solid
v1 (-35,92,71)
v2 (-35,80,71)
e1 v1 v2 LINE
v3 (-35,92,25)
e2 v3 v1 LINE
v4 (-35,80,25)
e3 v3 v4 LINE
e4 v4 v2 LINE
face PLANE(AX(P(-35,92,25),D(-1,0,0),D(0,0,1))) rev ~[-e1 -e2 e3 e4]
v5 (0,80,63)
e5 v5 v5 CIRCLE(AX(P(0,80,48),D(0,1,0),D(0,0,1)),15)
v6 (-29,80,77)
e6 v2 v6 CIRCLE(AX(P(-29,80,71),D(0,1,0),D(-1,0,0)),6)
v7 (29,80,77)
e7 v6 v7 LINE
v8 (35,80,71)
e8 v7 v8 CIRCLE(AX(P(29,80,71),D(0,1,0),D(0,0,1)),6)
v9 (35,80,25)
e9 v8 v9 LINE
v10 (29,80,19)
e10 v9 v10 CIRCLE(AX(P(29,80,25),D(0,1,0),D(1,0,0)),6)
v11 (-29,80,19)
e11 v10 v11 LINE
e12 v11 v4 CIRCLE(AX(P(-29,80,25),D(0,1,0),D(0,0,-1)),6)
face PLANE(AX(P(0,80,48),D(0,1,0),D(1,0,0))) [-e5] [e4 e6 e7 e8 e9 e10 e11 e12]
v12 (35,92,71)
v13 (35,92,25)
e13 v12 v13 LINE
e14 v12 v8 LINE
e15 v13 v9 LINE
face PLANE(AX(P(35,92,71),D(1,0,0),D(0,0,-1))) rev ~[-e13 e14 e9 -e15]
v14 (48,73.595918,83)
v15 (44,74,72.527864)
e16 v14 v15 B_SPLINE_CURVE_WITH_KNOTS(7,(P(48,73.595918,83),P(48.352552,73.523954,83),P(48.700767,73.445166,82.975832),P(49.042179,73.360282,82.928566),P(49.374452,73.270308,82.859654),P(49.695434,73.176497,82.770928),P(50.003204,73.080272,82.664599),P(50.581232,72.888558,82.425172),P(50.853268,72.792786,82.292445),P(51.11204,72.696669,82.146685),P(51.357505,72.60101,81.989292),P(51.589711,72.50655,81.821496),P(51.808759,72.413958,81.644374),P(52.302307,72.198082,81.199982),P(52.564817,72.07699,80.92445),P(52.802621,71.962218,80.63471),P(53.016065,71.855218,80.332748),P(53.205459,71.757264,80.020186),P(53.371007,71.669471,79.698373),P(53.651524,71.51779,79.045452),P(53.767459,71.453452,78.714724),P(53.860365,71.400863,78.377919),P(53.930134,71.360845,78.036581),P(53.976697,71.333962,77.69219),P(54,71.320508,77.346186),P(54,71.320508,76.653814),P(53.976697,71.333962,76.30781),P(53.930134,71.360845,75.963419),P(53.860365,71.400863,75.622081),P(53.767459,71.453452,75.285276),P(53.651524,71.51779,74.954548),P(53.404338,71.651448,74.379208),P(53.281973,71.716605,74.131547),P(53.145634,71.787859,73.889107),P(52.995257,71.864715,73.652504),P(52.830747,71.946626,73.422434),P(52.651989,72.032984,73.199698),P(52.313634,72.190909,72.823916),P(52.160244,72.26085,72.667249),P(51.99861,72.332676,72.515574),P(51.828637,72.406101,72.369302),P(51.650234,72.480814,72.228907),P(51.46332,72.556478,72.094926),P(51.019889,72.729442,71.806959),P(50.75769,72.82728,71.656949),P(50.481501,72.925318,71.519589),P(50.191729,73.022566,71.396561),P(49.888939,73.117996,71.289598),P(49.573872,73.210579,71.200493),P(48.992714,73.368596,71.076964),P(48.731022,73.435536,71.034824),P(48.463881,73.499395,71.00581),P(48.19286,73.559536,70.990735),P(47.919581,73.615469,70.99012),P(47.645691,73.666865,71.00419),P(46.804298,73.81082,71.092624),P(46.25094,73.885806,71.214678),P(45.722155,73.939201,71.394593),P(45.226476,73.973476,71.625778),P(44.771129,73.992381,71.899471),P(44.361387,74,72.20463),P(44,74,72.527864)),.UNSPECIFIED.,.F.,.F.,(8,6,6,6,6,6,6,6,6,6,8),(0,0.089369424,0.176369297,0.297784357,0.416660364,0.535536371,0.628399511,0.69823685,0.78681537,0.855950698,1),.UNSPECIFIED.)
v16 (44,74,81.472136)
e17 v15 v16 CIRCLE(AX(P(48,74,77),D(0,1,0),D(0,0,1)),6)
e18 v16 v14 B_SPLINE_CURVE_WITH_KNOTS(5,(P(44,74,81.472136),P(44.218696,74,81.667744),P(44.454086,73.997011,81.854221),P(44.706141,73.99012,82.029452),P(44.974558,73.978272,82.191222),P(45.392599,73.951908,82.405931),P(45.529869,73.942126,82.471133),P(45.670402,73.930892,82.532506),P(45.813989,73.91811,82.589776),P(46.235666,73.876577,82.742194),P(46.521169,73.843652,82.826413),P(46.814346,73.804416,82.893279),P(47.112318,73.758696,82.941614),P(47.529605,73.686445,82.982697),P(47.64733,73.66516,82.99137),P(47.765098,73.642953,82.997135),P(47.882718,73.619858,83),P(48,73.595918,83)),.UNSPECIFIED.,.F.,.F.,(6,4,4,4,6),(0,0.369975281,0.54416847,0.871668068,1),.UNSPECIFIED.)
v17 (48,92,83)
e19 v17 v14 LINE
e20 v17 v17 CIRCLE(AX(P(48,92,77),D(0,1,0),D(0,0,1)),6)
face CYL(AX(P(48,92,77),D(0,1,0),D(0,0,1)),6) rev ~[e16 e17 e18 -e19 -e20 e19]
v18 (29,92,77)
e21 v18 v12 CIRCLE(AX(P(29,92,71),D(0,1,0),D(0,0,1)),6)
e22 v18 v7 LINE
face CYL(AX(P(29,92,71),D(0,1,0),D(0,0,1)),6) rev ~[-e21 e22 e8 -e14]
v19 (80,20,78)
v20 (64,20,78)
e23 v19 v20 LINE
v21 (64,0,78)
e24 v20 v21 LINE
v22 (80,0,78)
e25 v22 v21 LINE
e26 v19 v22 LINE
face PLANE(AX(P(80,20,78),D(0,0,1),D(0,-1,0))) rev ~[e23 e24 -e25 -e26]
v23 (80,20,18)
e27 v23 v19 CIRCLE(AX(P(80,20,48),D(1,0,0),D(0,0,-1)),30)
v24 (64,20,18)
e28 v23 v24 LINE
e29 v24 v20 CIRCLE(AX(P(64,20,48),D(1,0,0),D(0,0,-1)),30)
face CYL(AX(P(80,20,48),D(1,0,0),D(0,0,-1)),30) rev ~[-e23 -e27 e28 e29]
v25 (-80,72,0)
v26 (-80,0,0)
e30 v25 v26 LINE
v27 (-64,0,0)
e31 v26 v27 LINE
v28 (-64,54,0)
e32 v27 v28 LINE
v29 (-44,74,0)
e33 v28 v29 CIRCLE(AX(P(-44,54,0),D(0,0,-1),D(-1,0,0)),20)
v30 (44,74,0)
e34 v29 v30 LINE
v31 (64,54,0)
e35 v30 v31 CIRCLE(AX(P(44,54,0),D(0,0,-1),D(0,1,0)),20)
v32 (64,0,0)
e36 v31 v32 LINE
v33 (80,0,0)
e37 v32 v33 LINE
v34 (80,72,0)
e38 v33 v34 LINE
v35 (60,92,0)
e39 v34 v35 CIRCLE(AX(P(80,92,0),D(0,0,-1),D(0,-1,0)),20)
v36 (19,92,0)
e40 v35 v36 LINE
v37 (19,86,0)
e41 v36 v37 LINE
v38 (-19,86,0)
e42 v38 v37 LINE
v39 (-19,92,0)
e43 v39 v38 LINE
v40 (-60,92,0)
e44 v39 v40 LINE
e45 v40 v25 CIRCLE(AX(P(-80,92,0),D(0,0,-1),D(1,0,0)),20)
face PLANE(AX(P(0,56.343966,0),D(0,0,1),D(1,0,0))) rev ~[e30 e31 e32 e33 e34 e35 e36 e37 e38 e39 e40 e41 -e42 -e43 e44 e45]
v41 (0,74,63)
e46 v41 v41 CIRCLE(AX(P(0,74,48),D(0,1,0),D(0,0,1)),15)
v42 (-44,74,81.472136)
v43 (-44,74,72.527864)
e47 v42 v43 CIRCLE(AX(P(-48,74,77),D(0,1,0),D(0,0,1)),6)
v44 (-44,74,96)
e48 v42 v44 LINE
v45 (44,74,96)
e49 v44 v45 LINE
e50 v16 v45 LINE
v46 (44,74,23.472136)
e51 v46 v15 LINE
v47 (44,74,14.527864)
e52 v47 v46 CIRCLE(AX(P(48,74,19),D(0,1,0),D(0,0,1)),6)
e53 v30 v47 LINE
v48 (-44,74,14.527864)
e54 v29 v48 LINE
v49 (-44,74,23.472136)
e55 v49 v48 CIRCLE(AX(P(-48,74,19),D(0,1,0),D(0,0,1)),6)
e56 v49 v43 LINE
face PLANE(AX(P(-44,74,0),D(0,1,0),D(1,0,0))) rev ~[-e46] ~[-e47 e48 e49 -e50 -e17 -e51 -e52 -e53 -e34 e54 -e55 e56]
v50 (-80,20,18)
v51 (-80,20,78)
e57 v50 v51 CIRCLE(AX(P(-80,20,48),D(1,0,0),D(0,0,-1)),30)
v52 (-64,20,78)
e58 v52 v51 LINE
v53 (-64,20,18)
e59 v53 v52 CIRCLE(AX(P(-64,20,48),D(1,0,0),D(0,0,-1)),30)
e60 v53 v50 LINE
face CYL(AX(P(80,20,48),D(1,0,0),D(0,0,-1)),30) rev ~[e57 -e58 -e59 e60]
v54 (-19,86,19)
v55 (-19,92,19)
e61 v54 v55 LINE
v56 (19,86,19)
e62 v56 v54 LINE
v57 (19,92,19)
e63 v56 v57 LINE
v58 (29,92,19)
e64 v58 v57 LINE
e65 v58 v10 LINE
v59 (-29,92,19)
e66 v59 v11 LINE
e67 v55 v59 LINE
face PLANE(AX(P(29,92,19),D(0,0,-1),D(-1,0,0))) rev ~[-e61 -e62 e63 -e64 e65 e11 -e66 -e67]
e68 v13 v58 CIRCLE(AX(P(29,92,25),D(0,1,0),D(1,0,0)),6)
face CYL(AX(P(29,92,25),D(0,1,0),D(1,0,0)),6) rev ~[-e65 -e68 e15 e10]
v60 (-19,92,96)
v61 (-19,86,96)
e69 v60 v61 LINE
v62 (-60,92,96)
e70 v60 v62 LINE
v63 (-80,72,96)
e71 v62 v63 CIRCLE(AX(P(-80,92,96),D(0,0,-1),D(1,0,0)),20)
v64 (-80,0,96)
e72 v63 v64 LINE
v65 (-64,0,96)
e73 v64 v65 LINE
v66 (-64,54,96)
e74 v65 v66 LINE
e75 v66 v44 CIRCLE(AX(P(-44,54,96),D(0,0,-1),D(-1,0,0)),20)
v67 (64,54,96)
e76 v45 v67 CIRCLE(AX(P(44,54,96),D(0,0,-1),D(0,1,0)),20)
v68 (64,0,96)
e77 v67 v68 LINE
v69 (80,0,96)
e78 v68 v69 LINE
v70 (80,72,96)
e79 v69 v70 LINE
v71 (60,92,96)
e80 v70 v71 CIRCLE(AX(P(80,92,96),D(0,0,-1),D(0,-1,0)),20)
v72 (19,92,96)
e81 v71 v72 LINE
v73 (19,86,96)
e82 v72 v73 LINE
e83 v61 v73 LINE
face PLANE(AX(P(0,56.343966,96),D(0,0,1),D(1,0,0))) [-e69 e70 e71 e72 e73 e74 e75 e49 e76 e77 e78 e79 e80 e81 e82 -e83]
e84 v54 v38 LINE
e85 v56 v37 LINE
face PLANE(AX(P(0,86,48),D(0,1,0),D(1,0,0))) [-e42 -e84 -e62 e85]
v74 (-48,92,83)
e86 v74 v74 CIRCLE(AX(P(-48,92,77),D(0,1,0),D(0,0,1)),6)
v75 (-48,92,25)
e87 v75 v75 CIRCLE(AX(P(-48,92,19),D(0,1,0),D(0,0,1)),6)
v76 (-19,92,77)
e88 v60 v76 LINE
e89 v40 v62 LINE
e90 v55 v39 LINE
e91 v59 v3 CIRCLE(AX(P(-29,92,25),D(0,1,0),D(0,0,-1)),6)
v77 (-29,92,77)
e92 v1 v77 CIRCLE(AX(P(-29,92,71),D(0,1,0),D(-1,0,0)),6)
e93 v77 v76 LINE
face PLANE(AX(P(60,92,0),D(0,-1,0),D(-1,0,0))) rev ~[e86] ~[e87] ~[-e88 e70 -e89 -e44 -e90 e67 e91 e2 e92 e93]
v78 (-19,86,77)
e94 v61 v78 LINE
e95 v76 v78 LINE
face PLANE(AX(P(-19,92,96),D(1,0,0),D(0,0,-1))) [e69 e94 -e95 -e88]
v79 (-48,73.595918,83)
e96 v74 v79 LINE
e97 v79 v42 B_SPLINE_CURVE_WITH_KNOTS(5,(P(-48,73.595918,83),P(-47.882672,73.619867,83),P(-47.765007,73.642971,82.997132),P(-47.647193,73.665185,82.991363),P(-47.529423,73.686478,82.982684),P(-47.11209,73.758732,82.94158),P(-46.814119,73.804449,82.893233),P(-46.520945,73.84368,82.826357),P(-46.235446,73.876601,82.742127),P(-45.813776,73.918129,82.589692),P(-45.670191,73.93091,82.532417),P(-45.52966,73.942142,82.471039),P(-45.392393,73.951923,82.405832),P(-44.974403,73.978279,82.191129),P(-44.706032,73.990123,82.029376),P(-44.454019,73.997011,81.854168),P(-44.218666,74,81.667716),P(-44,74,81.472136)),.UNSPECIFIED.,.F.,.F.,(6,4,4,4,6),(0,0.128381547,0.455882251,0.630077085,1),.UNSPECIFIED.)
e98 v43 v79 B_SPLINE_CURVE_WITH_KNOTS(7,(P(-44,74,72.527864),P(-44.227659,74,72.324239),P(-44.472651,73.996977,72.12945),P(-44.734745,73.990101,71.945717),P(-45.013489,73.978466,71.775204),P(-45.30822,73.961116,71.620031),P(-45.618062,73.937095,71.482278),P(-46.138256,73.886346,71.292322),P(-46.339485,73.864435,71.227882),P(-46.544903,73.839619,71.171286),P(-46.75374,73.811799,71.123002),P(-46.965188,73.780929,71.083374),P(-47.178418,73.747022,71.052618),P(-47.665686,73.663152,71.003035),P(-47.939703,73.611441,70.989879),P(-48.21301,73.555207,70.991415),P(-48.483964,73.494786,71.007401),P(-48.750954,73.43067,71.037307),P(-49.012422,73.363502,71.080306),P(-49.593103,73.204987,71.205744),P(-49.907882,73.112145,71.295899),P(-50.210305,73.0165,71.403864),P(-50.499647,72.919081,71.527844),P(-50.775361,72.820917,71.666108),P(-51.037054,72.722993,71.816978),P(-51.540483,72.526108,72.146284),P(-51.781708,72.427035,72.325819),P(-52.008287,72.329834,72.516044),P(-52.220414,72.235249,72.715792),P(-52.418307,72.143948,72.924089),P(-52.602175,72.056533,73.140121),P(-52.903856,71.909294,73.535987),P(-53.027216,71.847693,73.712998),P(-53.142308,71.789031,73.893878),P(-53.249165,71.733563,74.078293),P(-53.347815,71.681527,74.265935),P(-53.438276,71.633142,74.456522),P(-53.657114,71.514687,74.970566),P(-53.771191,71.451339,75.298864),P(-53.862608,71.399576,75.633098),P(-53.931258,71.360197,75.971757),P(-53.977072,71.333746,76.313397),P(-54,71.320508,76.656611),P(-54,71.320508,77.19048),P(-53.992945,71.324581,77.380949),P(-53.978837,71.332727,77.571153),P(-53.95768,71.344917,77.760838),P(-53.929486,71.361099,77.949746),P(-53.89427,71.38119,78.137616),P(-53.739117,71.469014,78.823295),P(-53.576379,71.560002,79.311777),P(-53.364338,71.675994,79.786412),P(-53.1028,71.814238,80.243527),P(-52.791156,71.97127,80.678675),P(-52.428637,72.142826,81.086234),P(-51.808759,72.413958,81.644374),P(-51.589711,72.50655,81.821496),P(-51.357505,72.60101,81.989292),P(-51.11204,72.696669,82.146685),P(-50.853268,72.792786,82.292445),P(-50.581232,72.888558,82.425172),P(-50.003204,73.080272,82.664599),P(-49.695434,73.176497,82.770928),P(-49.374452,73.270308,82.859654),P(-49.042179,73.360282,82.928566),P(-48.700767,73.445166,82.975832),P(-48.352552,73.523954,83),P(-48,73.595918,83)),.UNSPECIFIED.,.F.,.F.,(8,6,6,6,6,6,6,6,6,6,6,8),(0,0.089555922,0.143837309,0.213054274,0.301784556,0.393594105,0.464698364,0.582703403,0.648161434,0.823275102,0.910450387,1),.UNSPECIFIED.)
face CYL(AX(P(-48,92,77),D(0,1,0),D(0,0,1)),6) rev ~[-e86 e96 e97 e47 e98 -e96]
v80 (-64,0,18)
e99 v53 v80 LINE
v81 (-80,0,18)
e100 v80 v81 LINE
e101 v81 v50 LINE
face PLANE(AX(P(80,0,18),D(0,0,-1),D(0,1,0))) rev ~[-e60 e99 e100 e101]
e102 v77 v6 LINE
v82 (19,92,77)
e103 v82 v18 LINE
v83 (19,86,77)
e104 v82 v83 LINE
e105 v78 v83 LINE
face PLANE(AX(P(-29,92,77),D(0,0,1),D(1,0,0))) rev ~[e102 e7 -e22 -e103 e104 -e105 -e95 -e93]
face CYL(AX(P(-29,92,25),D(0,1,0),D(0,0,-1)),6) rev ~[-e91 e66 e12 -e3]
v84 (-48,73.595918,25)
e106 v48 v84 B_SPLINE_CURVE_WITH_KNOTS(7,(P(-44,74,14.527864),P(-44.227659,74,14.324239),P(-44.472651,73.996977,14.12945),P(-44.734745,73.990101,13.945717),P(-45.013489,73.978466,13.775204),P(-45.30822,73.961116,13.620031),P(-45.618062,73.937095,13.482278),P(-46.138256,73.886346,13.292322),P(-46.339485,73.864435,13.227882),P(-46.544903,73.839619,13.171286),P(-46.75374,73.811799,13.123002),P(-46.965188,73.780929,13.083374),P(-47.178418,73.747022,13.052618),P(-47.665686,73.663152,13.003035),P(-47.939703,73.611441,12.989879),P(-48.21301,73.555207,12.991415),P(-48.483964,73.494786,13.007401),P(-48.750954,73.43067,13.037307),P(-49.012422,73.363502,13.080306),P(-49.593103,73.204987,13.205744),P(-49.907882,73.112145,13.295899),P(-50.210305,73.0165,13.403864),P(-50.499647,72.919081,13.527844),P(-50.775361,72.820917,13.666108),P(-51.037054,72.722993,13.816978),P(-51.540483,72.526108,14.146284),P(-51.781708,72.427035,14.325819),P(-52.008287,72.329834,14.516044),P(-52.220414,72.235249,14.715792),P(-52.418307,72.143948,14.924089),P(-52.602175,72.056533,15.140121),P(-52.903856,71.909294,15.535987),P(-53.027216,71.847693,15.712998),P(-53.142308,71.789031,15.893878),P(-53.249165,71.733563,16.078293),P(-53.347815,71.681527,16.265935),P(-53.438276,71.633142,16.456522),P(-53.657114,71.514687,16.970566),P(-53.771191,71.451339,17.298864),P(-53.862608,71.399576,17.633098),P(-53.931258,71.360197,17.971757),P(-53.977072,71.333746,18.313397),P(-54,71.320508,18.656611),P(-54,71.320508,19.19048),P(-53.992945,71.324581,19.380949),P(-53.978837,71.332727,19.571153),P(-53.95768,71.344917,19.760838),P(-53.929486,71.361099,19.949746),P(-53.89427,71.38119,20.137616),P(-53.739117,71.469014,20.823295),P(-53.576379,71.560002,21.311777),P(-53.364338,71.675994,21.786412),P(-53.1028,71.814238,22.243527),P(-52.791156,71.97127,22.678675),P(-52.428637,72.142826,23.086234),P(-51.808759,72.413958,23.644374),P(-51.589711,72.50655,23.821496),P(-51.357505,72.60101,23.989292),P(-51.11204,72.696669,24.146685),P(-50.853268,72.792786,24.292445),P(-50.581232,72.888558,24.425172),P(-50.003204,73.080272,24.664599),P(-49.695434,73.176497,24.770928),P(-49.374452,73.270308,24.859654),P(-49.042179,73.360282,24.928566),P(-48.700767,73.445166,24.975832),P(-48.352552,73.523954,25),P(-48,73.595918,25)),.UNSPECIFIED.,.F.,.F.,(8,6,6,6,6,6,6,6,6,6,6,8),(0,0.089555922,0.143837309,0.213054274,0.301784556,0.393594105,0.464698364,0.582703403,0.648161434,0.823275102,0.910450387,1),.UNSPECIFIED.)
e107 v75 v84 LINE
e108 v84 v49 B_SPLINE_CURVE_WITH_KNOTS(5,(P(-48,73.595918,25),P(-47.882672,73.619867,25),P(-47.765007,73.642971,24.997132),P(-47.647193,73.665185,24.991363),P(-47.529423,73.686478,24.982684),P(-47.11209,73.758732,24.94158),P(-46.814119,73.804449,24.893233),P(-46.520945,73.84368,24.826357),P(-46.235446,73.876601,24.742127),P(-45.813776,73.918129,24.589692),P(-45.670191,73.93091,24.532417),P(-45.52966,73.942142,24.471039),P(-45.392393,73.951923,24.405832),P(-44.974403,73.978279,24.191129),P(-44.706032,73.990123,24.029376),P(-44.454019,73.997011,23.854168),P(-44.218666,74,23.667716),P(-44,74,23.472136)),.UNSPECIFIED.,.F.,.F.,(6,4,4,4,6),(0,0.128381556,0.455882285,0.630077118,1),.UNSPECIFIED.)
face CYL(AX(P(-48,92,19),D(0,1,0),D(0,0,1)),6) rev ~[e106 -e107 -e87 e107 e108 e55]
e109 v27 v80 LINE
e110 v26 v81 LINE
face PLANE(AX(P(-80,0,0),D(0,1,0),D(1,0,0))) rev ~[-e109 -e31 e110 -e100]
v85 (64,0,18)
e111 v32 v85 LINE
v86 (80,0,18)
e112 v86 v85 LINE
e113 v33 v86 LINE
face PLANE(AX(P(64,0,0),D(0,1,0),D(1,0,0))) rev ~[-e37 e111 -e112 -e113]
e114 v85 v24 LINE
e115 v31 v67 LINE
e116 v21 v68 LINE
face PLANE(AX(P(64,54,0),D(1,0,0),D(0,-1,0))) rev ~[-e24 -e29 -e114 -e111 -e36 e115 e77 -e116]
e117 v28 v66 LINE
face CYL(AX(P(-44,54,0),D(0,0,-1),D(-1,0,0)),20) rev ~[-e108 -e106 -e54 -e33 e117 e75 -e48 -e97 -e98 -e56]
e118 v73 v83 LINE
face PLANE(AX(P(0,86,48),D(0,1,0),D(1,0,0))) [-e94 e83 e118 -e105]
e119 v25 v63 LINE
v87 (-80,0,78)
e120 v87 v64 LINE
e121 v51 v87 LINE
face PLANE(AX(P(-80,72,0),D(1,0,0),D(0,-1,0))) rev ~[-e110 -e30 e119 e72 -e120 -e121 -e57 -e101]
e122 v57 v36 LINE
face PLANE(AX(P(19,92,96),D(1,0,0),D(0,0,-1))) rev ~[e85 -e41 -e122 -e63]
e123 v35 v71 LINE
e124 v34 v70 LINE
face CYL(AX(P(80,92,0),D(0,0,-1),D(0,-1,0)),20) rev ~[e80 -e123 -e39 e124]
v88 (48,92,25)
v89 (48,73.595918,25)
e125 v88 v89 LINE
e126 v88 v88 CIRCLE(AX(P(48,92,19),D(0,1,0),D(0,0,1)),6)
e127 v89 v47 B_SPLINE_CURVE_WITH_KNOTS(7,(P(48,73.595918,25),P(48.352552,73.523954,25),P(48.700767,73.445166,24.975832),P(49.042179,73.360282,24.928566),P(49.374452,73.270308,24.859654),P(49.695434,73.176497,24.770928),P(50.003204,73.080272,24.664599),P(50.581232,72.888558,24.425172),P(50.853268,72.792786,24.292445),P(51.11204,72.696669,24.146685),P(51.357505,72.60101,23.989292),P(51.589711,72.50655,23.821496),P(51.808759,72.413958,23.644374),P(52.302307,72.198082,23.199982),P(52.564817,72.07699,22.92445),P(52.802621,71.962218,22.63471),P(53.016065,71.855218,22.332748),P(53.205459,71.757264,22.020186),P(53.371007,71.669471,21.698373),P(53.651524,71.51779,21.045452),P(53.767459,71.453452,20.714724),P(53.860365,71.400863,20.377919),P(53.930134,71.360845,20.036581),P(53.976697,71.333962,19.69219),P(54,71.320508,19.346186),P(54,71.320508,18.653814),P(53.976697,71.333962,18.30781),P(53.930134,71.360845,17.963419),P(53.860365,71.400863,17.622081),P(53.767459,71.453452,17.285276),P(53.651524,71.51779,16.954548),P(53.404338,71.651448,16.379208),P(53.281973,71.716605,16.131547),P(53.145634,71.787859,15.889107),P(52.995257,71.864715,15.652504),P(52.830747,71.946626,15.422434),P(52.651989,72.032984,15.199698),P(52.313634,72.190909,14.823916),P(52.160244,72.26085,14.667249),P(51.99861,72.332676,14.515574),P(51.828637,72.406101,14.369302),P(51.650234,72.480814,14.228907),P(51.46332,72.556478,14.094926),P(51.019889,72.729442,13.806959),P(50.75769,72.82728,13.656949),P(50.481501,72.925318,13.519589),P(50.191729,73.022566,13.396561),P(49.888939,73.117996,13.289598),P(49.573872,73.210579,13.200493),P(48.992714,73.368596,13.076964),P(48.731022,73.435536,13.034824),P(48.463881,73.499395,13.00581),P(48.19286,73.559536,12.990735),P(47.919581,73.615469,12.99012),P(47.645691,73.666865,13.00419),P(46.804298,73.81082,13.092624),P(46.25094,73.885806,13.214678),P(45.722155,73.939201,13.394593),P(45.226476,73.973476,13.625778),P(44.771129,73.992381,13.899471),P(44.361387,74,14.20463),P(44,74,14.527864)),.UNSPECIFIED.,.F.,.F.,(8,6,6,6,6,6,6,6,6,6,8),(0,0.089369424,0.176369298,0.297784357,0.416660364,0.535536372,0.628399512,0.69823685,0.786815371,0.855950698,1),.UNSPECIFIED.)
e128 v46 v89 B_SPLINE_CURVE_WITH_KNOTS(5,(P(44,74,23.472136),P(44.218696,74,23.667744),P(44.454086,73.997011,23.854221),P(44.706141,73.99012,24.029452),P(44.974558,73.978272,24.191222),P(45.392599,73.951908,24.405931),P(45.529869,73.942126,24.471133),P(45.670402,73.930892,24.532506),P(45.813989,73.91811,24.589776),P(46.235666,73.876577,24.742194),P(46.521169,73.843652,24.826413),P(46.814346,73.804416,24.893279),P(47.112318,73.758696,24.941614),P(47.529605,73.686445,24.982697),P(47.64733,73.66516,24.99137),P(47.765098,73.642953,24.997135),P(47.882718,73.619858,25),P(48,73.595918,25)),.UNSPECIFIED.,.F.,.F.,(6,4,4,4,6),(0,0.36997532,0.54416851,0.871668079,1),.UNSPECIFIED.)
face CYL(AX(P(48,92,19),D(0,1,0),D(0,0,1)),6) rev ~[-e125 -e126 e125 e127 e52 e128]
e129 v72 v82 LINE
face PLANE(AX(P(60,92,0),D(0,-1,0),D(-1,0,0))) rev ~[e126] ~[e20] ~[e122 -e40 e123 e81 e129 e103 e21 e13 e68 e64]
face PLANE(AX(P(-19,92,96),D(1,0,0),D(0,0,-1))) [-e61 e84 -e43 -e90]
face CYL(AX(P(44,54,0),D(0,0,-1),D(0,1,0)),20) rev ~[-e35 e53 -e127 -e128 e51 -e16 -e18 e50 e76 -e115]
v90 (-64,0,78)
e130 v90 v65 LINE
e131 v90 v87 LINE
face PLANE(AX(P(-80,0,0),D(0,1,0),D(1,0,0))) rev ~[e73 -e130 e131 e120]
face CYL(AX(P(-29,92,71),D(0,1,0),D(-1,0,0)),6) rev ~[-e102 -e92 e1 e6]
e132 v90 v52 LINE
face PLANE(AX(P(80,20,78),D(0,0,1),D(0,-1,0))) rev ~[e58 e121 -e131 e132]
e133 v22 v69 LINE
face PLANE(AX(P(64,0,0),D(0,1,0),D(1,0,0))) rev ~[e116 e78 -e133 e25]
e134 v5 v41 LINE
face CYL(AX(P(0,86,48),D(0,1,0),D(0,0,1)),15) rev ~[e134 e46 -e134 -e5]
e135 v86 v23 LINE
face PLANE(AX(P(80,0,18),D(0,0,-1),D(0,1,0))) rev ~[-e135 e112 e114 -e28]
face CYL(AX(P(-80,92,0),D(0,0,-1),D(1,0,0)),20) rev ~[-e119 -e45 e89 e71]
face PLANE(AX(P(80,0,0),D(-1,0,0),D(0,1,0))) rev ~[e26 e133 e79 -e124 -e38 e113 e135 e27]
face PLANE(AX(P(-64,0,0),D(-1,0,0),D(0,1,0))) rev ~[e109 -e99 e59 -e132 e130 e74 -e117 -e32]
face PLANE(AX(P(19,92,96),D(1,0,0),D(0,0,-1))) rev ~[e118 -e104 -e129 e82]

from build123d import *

# Parameters (mm, degrees)
BRIDGE_BODY_DEPTH          = 96
ARCH_RELIEF_CUT_DEPTH      = 209.038457983
TOP_CHANNEL_SKETCH_W       = 38
TOP_CHANNEL_SKETCH_H       = 96
TOP_CHANNEL_38X6_DEPTH     = 6
CENTER_BORE_SKETCH_R       = 15
CENTER_BORE_30_DEPTH       = 152.69706655
MOUNTING_HOLES_SKETCH_R    = 6
MOUNTING_HOLES_4X_12_DEPTH = 156.17731793
CENTER_POCKET_58X70_DEPTH  = 12


with BuildPart() as part:
    # Bridge Profile Sketch → Bridge Body (new body)
    with BuildSketch(Plane.XY):
        with BuildLine():
            Line((-80, 0), (-64, 0))
            Line((-64, 0), (-64, 54))
            ThreePointArc((-64, 54), (-58.142135624, 68.142135624), (-44, 74))
            Line((-44, 74), (44, 74))
            ThreePointArc((44, 74), (58.142135624, 68.142135624), (64, 54))
            Line((64, 54), (64, 0))
            Line((64, 0), (80, 0))
            Line((80, 0), (80, 72))
            ThreePointArc((80, 72), (65.857864376, 77.857864376), (60, 92))
            Line((60, 92), (-60, 92))
            ThreePointArc((-60, 92), (-65.857864376, 77.857864376), (-80, 72))
            Line((-80, 72), (-80, 0))
        make_face()
    extrude(amount=BRIDGE_BODY_DEPTH)

    # Arch Relief Sketch → Arch Relief Cut (cut, through all)
    with BuildSketch(Plane(origin=(80, 0, 0), x_dir=(0, 0, -1), z_dir=(1, 0, 0))):
        with BuildLine():
            Line((-78, 20), (-78, 0))
            Line((-78, 0), (-18, 0))
            Line((-18, 0), (-18, 20))
            ThreePointArc((-18, 20), (-48, 50), (-78, 20))
        make_face()
    extrude(amount=-ARCH_RELIEF_CUT_DEPTH, mode=Mode.SUBTRACT)

    # Top Channel Sketch → Top Channel 38x6 (cut)
    with BuildSketch(Plane(origin=(0, 92, 0), x_dir=(1, 0, 0), z_dir=(0, 1, 0))):
        with Locations((0, -48)):
            Rectangle(TOP_CHANNEL_SKETCH_W, TOP_CHANNEL_SKETCH_H)
    extrude(amount=-TOP_CHANNEL_38X6_DEPTH, mode=Mode.SUBTRACT)

    # Center Bore Sketch → Center Bore Ø30 (cut, through all)
    with BuildSketch(Plane(origin=(0, 86, 0), x_dir=(1, 0, 0), z_dir=(0, 1, 0))):
        with Locations(Location((0, -48, 0), (0, 0, 270))):
            Circle(CENTER_BORE_SKETCH_R)
    extrude(amount=-CENTER_BORE_30_DEPTH, mode=Mode.SUBTRACT)

    # Mounting Holes Sketch → Mounting Holes 4xØ12 (cut, through all)
    with BuildSketch(Plane(origin=(0, 92, 0), x_dir=(1, 0, 0), z_dir=(0, 1, 0))):
        with Locations(Location((-48, -19, 0), (0, 0, 270))):
            Circle(MOUNTING_HOLES_SKETCH_R)
        with Locations(Location((48, -19, 0), (0, 0, 270))):
            Circle(MOUNTING_HOLES_SKETCH_R)
        with Locations(Location((48, -77, 0), (0, 0, 270))):
            Circle(MOUNTING_HOLES_SKETCH_R)
        with Locations(Location((-48, -77, 0), (0, 0, 270))):
            Circle(MOUNTING_HOLES_SKETCH_R)
    extrude(amount=-MOUNTING_HOLES_4X_12_DEPTH, mode=Mode.SUBTRACT)

    # Center Pocket Sketch → Center Pocket 58x70 (cut)
    with BuildSketch(Plane(origin=(0, 92, 0), x_dir=(1, 0, 0), z_dir=(0, 1, 0))):
        with BuildLine():
            Line((-29, -77), (29, -77))
            ThreePointArc((29, -77), (33.242640687, -75.242640687), (35, -71))
            Line((35, -71), (35, -25))
            ThreePointArc((35, -25), (33.242640687, -20.757359313), (29, -19))
            Line((29, -19), (-29, -19))
            ThreePointArc((-29, -19), (-33.242640687, -20.757359313), (-35, -25))
            Line((-35, -25), (-35, -71))
            ThreePointArc((-35, -71), (-33.242640687, -75.242640687), (-29, -77))
        make_face()
    extrude(amount=-CENTER_POCKET_58X70_DEPTH, mode=Mode.SUBTRACT)


solid = part.part
